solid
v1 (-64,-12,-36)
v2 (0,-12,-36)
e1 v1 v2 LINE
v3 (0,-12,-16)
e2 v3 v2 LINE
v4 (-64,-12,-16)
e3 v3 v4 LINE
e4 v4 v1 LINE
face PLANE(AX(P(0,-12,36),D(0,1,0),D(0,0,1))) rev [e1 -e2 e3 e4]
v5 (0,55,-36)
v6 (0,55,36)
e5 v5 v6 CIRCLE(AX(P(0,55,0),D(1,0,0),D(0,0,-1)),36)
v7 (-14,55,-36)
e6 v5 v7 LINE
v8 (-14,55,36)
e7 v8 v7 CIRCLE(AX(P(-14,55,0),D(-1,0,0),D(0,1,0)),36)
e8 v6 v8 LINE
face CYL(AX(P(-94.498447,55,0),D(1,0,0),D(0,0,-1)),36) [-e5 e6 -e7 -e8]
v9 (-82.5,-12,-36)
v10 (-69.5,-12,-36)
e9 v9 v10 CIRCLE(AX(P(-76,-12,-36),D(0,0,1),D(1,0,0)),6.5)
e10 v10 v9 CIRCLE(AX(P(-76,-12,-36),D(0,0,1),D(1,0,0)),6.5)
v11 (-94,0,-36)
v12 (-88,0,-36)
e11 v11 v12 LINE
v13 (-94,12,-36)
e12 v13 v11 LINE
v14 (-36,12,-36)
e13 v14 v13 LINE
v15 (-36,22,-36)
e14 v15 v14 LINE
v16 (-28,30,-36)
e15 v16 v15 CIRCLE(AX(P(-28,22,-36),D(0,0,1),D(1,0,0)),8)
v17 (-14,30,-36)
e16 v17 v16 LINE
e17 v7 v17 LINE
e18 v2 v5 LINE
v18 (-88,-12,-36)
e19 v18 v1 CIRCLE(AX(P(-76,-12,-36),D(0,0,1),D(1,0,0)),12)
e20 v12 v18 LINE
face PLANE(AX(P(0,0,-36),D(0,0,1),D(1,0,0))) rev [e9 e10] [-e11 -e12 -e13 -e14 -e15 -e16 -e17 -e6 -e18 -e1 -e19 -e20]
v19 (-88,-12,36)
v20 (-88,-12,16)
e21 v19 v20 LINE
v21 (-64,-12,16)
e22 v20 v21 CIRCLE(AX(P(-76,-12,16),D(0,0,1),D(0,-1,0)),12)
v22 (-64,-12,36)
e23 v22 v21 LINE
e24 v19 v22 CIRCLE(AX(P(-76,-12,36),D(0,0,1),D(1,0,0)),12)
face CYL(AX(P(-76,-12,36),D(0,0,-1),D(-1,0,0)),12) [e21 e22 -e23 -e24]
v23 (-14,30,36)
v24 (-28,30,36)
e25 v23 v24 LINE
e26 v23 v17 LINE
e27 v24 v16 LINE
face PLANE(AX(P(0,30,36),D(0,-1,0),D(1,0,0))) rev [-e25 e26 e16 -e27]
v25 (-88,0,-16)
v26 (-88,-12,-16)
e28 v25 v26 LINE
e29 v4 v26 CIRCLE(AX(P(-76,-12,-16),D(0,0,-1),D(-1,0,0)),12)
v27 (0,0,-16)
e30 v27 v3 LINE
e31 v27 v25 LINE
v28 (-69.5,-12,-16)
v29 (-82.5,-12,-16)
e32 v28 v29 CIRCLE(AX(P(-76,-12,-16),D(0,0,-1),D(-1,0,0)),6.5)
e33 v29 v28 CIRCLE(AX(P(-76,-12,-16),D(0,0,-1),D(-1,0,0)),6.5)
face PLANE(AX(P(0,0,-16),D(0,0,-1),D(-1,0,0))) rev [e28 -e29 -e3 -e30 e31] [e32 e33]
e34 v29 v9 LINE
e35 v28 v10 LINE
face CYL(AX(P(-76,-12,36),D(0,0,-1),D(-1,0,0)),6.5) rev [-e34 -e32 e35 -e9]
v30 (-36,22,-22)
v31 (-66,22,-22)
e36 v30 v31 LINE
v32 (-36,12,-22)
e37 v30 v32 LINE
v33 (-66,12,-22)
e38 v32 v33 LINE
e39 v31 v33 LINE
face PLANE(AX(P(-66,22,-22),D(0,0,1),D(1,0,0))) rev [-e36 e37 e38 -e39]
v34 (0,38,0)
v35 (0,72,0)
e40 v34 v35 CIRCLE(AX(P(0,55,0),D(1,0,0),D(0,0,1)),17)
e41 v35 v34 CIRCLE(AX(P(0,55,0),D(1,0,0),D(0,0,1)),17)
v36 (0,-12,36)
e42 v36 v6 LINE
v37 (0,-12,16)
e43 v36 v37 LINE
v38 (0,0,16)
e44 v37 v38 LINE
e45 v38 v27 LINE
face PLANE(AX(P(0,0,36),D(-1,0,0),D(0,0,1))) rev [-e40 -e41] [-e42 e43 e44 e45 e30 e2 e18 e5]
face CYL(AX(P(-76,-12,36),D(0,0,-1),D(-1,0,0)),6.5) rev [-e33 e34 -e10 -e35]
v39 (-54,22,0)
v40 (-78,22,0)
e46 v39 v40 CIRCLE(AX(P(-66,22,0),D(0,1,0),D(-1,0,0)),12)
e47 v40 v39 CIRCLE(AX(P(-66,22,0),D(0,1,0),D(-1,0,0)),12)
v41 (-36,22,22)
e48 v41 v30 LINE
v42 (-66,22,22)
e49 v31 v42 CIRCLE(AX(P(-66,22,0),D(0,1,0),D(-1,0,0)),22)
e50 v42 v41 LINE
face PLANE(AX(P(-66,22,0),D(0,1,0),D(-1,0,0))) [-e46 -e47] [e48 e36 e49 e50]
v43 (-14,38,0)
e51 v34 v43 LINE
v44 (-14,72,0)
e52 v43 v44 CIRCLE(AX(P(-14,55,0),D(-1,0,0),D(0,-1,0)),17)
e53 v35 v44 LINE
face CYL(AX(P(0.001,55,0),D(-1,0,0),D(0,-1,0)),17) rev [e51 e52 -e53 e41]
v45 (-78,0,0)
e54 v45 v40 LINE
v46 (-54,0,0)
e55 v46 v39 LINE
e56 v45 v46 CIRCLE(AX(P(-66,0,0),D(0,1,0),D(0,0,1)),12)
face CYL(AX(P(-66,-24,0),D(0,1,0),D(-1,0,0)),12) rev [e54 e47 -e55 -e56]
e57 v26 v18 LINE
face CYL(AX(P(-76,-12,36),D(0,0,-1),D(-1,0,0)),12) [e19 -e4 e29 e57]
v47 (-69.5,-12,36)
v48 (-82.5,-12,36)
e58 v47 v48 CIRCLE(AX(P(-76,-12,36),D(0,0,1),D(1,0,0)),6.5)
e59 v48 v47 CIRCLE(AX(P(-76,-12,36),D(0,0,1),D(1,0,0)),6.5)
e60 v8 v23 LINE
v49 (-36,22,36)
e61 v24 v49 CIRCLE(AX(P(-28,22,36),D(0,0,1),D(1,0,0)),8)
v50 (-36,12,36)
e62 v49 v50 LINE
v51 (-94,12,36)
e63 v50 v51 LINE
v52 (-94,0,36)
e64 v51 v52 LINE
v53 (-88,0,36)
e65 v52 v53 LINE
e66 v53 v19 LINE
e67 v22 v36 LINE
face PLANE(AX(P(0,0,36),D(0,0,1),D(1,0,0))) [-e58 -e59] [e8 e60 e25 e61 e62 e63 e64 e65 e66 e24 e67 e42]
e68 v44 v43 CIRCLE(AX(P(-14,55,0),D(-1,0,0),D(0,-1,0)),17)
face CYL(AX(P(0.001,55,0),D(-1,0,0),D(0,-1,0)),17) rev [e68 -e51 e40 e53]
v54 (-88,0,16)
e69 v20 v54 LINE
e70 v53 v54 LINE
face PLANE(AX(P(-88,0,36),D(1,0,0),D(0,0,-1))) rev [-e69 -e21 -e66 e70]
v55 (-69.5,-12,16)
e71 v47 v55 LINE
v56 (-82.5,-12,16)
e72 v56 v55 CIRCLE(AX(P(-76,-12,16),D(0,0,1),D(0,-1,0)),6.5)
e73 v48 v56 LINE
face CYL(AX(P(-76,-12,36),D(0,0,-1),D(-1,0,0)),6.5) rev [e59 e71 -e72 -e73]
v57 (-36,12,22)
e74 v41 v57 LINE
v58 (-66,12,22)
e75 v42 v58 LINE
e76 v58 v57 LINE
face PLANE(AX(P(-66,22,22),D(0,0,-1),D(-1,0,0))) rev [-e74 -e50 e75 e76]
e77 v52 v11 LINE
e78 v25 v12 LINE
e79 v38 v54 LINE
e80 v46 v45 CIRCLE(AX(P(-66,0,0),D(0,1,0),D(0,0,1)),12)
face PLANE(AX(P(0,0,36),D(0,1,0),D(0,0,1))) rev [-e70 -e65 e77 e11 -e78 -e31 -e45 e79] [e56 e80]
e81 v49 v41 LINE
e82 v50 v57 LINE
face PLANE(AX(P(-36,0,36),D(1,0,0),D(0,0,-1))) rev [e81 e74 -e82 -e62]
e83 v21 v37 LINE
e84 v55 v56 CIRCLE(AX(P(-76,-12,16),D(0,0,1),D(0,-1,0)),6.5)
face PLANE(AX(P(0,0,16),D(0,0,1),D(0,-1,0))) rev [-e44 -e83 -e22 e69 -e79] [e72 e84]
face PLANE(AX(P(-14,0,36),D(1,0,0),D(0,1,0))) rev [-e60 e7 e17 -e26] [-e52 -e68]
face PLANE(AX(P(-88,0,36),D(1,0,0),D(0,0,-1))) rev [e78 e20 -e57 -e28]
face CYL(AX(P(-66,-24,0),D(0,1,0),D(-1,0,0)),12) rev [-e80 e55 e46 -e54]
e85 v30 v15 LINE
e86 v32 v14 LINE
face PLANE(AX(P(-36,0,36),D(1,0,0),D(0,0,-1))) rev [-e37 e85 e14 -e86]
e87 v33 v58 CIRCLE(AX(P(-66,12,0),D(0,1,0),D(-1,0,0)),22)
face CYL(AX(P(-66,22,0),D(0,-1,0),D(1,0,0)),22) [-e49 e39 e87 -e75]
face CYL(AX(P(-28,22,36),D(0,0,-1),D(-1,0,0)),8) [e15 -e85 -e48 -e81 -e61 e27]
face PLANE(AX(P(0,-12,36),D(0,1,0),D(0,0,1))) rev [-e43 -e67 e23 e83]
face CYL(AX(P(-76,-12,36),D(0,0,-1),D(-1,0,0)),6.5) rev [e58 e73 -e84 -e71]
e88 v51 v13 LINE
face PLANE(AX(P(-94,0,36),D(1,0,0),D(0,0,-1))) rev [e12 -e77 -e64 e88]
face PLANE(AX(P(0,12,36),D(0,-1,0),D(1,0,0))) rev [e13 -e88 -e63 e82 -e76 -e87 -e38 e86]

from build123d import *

# Parameters (mm, degrees)
BASE_BODY_PROFILE_R   = 6.5
BASE_BODY_DEPTH       = 36
POCKET_32X20_SKETCH_W = 32
POCKET_32X20_SKETCH_H = 24
POCKET_32X20_DEPTH    = 110.840793879
LUG_ROUNDED_TOP_DEPTH = 14
LUG_BORE_34_REACH     = 128.4
LUG_BORE_SKETCH_R     = 17
BOSS_10MM_DEPTH       = 10
BOSS_BORE_SKETCH_R    = 12
BOSS_BORE_24_DEPTH    = 123.036879672


with BuildPart() as part:
    # Base Body Profile → Base Body (new, symmetric)
    with BuildSketch(Plane.XY):
        with BuildLine():
            Line((0, -12), (0, 0))
            Line((0, 0), (0, 55))
            Line((0, 55), (-14, 55))
            Line((-14, 55), (-14, 30))
            Line((-14, 30), (-28, 30))
            ThreePointArc((-28, 30), (-33.656854249, 27.656854249), (-36, 22))
            Line((-36, 22), (-36, 12))
            Line((-36, 12), (-94, 12))
            Line((-94, 12), (-94, 0))
            Line((-94, 0), (-88, 0))
            Line((-88, 0), (-88, -12))
            ThreePointArc((-88, -12), (-76, -24), (-64, -12))
            Line((-64, -12), (0, -12))
        make_face()
        with Locations((-76, -12)):
            Circle(BASE_BODY_PROFILE_R, mode=Mode.SUBTRACT)
    extrude(amount=BASE_BODY_DEPTH, both=True)

    # Pocket 32x20 Sketch → Pocket 32x20 (cut, through all)
    with BuildSketch(Plane.ZY.offset(88)):
        with Locations((0, -12)):
            Rectangle(POCKET_32X20_SKETCH_W, POCKET_32X20_SKETCH_H)
    extrude(amount=-POCKET_32X20_DEPTH, mode=Mode.SUBTRACT)

    # Lug Rounded Top Sketch → Lug Rounded Top (add)
    with BuildSketch(Plane(origin=(0, 0, 0), x_dir=(0, 0, -1), z_dir=(1, 0, 0))):
        with BuildLine():
            Line((-36, 55), (36, 55))
            ThreePointArc((36, 55), (0, 91), (-36, 55))
        make_face()
    extrude(amount=-LUG_ROUNDED_TOP_DEPTH)

    # Lug Bore Sketch → Lug Bore Ø34 (cut, up to next)
    with BuildSketch(Plane.ZY.offset(14), mode=Mode.PRIVATE) as lug_bore_34_sk1:
        with Locations(Location((0, 55, 0), (0, 0, 270))):
            Circle(LUG_BORE_SKETCH_R)
    lug_bore_34_tool1 = extrude(lug_bore_34_sk1.sketch, amount=-LUG_BORE_34_REACH, mode=Mode.PRIVATE) & part.part
    add(lug_bore_34_tool1.solids().sort_by_distance((-14, 55, 0))[0], mode=Mode.SUBTRACT)

    # Boss Profile 44x30 → Boss 10mm (add)
    with BuildSketch(Plane(origin=(0, 12, 0), x_dir=(1, 0, 0), z_dir=(0, 1, 0))):
        with BuildLine():
            Line((-66, 22), (-36, 22))
            Line((-36, 22), (-36, -22))
            Line((-36, -22), (-66, -22))
            ThreePointArc((-66, -22), (-88, 0), (-66, 22))
        make_face()
    extrude(amount=BOSS_10MM_DEPTH)

    # Boss Bore Sketch → Boss Bore Ø24 (cut, through all)
    with BuildSketch(Plane(origin=(0, 22, 0), x_dir=(1, 0, 0), z_dir=(0, 1, 0))):
        with Locations(Location((-66, 0, 0), (0, 0, 180))):
            Circle(BOSS_BORE_SKETCH_R)
    extrude(amount=-BOSS_BORE_24_DEPTH, mode=Mode.SUBTRACT)


solid = part.part
